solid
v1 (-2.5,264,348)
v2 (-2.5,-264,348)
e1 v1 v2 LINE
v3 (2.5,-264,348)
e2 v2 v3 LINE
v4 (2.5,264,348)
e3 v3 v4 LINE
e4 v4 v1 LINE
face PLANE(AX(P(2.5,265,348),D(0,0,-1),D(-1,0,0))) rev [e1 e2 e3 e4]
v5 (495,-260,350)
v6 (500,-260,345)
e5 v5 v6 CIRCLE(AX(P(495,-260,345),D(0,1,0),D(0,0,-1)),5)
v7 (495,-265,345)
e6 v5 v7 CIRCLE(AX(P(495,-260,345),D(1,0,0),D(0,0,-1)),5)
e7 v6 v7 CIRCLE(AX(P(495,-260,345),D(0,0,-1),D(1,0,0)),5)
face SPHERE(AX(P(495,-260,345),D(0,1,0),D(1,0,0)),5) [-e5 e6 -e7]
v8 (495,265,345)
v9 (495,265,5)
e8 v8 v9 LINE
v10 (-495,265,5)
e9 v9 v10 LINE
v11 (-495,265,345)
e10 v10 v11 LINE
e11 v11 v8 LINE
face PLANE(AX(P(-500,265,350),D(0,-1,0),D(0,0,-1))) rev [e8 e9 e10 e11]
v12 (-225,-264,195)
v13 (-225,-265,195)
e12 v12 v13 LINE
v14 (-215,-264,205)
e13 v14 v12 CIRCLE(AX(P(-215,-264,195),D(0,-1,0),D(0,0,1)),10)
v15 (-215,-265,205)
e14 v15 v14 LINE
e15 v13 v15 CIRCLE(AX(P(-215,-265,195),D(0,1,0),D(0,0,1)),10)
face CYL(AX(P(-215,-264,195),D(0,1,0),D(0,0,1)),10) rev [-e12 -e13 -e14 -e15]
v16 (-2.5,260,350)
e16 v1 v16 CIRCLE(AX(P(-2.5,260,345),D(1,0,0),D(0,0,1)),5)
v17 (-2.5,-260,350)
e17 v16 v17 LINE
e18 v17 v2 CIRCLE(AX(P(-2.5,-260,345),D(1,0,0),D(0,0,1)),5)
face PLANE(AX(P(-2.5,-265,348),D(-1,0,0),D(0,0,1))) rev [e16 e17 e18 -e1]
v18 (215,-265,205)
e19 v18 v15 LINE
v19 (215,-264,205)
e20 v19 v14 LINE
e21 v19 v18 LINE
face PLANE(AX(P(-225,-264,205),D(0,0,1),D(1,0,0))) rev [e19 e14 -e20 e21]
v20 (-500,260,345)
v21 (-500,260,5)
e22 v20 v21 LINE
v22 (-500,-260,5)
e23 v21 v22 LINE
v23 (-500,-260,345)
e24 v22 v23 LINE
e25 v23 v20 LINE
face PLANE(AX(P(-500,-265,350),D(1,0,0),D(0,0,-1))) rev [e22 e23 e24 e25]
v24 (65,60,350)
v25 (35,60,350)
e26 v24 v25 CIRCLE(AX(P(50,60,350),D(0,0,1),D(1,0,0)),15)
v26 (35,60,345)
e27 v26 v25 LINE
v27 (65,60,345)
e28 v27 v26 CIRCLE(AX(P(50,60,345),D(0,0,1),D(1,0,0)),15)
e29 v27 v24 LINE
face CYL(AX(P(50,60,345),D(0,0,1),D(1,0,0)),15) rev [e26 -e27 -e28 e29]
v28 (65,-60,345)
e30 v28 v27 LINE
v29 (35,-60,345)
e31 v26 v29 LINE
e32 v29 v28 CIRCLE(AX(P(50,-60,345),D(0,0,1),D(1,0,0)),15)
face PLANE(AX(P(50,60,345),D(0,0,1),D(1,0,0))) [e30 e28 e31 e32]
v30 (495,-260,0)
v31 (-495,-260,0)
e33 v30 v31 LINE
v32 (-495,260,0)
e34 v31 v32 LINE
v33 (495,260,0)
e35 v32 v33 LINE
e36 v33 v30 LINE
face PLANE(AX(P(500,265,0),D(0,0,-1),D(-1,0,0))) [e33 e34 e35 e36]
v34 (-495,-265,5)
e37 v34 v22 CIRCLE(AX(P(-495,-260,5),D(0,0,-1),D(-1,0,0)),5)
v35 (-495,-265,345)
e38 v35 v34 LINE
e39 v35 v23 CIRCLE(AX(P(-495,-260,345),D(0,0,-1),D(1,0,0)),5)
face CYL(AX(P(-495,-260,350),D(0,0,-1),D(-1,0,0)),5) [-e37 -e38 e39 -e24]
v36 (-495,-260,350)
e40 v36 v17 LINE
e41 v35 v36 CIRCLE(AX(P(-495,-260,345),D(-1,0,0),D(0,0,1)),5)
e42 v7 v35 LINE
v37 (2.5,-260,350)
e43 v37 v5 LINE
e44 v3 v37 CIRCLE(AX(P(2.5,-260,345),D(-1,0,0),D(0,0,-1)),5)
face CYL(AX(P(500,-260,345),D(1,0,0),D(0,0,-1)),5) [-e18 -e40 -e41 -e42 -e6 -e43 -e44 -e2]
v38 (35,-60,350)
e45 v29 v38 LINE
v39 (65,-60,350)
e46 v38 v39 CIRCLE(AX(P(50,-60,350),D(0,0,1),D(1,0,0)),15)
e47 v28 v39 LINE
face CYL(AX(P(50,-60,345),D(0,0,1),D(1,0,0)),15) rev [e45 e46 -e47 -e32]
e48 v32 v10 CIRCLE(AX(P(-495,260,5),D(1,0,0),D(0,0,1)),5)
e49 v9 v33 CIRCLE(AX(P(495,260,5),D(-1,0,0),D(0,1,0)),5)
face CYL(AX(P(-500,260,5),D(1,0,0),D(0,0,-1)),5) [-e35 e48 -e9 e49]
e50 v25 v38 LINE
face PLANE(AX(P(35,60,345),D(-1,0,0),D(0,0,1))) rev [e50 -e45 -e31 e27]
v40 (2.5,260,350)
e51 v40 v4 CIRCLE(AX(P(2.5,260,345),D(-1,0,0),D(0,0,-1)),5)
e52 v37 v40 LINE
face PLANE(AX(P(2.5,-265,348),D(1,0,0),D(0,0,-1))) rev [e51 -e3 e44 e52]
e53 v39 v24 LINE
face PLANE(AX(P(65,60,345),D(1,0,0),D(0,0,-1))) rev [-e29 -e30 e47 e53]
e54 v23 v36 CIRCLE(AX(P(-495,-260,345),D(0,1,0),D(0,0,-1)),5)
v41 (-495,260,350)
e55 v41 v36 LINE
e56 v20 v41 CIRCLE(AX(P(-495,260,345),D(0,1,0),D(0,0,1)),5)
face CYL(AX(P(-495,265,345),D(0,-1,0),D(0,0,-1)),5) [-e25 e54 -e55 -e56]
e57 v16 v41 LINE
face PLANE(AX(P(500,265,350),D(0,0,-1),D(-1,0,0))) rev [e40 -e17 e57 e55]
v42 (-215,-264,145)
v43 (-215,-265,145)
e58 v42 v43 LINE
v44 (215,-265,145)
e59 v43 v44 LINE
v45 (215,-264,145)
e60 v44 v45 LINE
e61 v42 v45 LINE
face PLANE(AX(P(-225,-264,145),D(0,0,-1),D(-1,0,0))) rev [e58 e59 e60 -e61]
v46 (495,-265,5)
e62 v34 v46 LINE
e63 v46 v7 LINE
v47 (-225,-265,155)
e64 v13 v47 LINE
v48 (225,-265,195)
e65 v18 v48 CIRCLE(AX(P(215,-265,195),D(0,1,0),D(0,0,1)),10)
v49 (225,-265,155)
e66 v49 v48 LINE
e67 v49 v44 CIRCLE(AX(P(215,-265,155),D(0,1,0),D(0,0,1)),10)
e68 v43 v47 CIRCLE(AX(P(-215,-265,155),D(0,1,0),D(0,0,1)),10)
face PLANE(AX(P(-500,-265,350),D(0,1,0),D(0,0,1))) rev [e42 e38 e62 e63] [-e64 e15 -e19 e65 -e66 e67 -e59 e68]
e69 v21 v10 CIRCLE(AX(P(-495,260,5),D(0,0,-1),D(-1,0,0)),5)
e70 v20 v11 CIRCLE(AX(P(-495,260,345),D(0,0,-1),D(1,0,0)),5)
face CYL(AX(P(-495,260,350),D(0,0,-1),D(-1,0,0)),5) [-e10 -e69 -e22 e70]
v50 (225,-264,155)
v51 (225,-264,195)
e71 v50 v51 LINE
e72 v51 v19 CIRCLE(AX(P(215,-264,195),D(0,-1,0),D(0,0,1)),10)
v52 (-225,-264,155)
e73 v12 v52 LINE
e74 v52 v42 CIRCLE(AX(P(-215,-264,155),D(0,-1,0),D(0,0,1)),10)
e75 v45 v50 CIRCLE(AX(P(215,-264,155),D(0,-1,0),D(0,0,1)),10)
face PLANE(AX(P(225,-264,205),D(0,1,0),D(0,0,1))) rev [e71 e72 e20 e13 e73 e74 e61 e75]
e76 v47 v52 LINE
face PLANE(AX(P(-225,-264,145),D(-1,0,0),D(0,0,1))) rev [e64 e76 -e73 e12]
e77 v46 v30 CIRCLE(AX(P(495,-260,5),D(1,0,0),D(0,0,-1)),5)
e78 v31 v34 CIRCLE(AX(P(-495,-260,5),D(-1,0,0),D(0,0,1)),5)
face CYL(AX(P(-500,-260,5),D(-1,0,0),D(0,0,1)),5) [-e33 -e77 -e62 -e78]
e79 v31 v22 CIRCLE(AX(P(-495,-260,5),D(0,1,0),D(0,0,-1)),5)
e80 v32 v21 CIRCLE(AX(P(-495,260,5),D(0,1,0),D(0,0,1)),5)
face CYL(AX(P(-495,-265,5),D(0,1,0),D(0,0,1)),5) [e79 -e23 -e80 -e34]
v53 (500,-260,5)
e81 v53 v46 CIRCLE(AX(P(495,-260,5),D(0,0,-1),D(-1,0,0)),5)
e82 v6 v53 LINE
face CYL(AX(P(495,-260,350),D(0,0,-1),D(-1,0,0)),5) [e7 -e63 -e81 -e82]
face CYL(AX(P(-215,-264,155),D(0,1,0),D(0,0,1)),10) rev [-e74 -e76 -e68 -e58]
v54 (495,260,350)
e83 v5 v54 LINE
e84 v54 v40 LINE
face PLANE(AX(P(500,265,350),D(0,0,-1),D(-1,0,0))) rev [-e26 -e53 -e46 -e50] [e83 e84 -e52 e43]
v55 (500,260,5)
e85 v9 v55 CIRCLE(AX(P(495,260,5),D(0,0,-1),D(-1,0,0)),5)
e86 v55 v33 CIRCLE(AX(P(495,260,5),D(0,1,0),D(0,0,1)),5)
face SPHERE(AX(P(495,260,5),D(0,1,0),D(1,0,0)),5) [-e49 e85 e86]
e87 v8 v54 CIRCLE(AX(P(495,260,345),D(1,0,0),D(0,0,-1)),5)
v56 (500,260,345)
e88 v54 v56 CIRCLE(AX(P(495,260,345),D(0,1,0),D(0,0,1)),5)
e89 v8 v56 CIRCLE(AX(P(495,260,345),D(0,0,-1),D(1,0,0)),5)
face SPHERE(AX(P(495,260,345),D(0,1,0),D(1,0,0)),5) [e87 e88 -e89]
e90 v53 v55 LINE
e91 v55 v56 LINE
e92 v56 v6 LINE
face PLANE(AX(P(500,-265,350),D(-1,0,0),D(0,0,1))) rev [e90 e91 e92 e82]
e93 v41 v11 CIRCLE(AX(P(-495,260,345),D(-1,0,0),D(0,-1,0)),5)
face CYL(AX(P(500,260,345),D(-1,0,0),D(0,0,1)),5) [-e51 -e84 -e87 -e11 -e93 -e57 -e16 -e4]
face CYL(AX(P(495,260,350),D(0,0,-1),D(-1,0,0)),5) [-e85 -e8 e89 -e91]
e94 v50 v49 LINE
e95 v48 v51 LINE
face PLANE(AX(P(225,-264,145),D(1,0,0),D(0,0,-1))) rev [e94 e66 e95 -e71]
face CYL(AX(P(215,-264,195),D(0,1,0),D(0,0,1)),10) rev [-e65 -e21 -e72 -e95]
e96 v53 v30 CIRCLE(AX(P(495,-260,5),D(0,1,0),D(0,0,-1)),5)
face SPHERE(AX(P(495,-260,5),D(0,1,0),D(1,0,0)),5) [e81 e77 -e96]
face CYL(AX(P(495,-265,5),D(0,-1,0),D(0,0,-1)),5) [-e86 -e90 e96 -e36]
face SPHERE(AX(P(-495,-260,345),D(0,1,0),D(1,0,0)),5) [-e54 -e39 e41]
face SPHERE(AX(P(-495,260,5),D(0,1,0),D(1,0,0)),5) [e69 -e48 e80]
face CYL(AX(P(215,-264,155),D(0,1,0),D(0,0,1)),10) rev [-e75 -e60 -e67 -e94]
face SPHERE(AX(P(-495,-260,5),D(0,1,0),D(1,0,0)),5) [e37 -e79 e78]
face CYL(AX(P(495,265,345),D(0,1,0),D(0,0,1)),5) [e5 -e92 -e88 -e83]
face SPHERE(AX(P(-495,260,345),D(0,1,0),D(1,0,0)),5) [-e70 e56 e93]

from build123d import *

# Parameters (mm, degrees)
SKETCH1_W           = 1000
SKETCH1_H           = 530
BOSS_EXTRUDE1_DEPTH = 350
FILLET1_R           = 5
SKETCH3_W           = 5
SKETCH3_H           = 530
CUT_EXTRUDE2_DEPTH  = 2
CUT_EXTRUDE3_DEPTH  = 5
SKETCH5_W           = 450
SKETCH5_H           = 60
CUT_EXTRUDE4_DEPTH  = 1
FILLET2_R           = 10


with BuildPart() as part:
    # Sketch1 → Boss-Extrude1 (new body)
    with BuildSketch(Plane.XY):
        Rectangle(SKETCH1_W, SKETCH1_H)
    extrude(amount=BOSS_EXTRUDE1_DEPTH)

    # Fillet1
    fillet1_edges = [part.edges().sort_by_distance(p)[0] for p in [
        (-500, 0, 350),
        (0, -265, 350),
        (500, 0, 350),
        (0, -265, 0),
        (-500, 0, 0),
        (0, 265, 0),
        (500, 0, 0),
        (0, 265, 350),
        (500, -265, 175),
        (-500, -265, 175),
        (-500, 265, 175),
        (500, 265, 175),
    ]]
    fillet(fillet1_edges, radius=FILLET1_R)

    # Sketch3 → Cut-Extrude2 (cut)
    with BuildSketch(Plane.XY.offset(350)):
        Rectangle(SKETCH3_W, SKETCH3_H)
    extrude(amount=-CUT_EXTRUDE2_DEPTH, mode=Mode.SUBTRACT)

    # Sketch4 → Cut-Extrude3 (cut)
    with BuildSketch(Plane.XY.offset(350)):
        with BuildLine():
            Line((65, 60), (65, -60))
            ThreePointArc((65, -60), (50, -75), (35, -60))
            Line((35, -60), (35, 60))
            ThreePointArc((35, 60), (50, 75), (65, 60))
        make_face()
    extrude(amount=-CUT_EXTRUDE3_DEPTH, mode=Mode.SUBTRACT)

    # Sketch5 → Cut-Extrude4 (cut)
    with BuildSketch(Plane.XZ.offset(265)):
        with Locations((0, 175)):
            Rectangle(SKETCH5_W, SKETCH5_H)
    extrude(amount=-CUT_EXTRUDE4_DEPTH, mode=Mode.SUBTRACT)

    # Fillet2
    fillet2_edges = [part.edges().sort_by_distance(p)[0] for p in [
        (225, -264.5, 205),
        (225, -264.5, 145),
        (-225, -264.5, 145),
        (-225, -264.5, 205),
    ]]
    fillet(fillet2_edges, radius=FILLET2_R)


solid = part.part
